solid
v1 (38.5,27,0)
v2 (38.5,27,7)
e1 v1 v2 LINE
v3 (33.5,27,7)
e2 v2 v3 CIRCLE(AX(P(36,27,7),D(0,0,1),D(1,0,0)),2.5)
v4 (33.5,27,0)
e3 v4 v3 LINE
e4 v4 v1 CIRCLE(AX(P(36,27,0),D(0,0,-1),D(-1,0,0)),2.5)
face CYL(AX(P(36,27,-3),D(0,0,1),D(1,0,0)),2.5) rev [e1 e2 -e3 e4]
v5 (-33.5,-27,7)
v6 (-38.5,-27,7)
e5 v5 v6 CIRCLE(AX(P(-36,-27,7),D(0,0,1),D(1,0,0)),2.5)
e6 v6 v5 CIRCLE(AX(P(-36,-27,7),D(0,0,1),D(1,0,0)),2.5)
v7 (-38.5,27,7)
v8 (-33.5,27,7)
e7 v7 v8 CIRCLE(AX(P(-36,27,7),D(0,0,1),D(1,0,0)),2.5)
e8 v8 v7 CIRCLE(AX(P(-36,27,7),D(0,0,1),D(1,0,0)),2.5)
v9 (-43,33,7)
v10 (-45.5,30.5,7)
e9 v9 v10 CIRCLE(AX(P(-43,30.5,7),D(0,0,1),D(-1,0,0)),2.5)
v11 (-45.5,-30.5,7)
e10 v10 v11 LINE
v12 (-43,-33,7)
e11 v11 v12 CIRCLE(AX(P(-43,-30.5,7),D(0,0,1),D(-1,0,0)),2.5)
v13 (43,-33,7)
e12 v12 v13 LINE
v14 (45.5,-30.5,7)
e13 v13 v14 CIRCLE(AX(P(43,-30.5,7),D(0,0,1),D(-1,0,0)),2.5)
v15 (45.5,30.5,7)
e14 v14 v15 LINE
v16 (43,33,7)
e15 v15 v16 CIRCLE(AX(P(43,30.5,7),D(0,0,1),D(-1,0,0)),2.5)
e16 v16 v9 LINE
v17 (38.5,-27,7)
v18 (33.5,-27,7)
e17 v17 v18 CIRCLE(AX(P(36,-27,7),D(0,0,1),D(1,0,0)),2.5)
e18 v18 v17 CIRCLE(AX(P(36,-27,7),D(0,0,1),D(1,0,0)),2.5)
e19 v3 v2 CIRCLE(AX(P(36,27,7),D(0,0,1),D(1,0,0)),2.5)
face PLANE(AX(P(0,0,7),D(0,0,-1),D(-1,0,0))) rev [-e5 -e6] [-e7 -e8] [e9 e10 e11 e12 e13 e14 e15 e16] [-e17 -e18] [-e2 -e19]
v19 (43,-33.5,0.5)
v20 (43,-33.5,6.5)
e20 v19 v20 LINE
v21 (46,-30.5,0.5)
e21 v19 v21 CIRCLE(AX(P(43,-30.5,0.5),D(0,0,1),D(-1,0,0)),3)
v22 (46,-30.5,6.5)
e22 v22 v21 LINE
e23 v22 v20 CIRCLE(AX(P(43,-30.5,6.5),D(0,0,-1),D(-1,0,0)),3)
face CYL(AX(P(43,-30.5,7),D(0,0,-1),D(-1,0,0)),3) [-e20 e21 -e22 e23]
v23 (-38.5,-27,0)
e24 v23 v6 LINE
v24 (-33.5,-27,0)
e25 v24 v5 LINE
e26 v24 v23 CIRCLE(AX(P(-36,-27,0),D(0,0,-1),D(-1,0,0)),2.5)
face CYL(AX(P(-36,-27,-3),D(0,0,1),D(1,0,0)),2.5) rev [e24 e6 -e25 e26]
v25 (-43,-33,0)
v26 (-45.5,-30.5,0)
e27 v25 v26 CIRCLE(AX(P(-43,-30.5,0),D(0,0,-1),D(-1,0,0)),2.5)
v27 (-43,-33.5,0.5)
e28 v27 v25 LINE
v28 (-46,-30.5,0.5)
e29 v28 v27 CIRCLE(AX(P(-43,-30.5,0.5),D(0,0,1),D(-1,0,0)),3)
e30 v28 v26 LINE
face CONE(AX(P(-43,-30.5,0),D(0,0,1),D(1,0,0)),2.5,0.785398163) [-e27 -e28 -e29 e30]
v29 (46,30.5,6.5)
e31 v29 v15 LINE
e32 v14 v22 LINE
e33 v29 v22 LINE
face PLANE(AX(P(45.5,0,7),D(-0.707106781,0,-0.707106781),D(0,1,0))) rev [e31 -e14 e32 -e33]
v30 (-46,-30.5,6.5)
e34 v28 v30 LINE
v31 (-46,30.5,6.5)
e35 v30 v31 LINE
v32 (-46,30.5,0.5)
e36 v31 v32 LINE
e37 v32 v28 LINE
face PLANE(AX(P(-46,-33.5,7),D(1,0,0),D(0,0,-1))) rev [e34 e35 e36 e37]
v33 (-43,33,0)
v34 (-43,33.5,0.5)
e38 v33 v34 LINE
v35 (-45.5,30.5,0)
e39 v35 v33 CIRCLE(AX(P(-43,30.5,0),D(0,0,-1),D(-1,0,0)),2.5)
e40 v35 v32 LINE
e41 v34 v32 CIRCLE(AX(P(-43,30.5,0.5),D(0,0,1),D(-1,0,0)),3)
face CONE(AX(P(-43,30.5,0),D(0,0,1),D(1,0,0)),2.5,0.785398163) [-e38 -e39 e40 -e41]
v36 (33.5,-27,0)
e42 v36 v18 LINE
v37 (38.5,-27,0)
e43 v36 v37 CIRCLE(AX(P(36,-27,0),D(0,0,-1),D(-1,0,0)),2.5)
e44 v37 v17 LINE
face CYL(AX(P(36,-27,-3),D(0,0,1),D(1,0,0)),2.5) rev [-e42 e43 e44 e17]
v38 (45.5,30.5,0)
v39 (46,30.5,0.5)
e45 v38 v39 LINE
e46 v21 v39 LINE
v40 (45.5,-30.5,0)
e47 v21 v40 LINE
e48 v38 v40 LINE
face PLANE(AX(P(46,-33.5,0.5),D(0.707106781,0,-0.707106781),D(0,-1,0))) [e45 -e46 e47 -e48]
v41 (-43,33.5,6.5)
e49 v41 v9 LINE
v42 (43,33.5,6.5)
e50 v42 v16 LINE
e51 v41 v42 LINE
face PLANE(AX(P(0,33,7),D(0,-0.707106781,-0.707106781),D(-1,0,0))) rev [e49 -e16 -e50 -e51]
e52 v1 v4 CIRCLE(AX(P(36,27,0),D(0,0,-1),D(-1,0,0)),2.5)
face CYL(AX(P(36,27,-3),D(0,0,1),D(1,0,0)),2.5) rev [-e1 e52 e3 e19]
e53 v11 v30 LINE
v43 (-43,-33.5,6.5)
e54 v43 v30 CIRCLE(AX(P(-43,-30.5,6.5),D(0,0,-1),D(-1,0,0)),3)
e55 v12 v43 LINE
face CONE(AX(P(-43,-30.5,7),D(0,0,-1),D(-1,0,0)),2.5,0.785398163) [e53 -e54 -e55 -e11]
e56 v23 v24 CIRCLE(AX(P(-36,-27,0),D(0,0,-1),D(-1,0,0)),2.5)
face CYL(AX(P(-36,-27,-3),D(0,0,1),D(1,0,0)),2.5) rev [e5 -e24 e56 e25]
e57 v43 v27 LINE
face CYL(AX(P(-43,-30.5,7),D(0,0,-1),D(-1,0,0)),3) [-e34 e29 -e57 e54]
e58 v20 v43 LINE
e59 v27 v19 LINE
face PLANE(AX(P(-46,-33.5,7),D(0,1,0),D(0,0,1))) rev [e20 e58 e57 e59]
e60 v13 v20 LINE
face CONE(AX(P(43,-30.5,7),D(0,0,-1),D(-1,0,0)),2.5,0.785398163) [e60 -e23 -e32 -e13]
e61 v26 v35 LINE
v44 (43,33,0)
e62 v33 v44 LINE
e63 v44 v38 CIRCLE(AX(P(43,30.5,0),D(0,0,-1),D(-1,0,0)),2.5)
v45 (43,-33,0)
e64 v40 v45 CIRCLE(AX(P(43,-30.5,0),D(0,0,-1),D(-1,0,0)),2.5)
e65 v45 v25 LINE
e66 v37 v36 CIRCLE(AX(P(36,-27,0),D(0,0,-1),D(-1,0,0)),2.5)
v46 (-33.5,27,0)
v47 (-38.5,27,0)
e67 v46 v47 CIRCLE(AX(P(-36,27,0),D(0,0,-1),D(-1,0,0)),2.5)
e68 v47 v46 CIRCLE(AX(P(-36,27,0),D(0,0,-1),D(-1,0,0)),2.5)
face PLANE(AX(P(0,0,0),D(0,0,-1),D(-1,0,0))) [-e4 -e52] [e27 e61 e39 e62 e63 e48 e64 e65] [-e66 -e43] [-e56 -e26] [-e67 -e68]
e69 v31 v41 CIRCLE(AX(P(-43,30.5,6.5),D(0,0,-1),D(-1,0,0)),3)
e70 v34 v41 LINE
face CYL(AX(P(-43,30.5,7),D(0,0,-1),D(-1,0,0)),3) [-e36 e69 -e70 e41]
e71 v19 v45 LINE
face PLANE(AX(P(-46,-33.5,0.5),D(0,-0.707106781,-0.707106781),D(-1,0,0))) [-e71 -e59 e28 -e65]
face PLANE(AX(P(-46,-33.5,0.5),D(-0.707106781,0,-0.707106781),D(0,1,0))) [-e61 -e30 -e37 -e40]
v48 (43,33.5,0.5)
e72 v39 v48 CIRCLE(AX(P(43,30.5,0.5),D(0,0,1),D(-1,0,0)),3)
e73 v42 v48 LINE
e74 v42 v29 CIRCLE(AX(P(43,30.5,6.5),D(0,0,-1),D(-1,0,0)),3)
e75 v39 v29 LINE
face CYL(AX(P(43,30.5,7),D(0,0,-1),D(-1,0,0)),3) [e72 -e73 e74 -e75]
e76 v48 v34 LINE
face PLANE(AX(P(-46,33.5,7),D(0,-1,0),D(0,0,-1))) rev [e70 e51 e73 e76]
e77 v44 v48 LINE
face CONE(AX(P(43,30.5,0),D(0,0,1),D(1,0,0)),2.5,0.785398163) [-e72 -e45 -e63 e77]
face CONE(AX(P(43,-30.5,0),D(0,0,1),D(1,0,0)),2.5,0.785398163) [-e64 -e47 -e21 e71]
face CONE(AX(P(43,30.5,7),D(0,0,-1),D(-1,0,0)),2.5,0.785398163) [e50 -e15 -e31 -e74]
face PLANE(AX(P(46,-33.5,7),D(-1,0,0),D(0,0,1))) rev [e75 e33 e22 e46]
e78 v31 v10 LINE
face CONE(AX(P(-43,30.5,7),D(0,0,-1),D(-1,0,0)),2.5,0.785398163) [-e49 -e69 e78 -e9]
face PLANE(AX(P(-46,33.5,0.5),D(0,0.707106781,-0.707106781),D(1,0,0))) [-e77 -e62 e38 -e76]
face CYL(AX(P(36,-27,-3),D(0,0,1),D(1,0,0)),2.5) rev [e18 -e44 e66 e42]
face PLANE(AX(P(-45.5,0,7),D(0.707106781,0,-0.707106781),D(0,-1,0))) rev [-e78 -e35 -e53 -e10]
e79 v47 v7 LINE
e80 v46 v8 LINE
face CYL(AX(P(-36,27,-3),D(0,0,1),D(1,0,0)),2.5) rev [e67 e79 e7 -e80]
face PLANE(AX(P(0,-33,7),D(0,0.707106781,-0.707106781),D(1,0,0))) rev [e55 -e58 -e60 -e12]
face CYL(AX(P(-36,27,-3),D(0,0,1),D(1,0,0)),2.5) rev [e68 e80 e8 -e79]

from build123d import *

# Parameters (mm, degrees)
SKETCH_1_W                  = 92
SKETCH_1_H                  = 67
EXTRUDE_1_DEPTH             = 7
FILLET_1_R                  = 3
SKETCH_2_R                  = 2.5
CUT_EXTRUDE_1_DEPTH         = 10
PATTERN_LINEAR_1_COUNT      = 2
PATTERN_LINEAR_1_PITCH      = 72
PATTERN_LINEAR_1_COUNT_DIR2 = 2
PATTERN_LINEAR_1_PITCH_DIR2 = 54
CHAMFER_1_SIZE              = 0.5


with BuildPart() as part:
    # 草图1 → 凸台-拉伸1 (new body)
    with BuildSketch(Plane.XY):
        Rectangle(SKETCH_1_W, SKETCH_1_H)
    extrude(amount=EXTRUDE_1_DEPTH)

    # 圆角1
    fillet_1_edges = [part.edges().sort_by_distance(p)[0] for p in [
        (46, -33.5, 3.5),
        (-46, -33.5, 3.5),
        (-46, 33.5, 3.5),
        (46, 33.5, 3.5),
    ]]
    fillet(fillet_1_edges, radius=FILLET_1_R)

    # 草图2 → 切除-拉伸1 (cut)
    with BuildSketch(Plane.XY.offset(7)):
        with Locations((-36, 27)):
            Circle(SKETCH_2_R)
    cut_extrude_1 = extrude(amount=-CUT_EXTRUDE_1_DEPTH, mode=Mode.SUBTRACT)

    # 阵列(线性)1: Cut-Extrude 1 2 × 2
    with Locations(*[(i * PATTERN_LINEAR_1_PITCH, -j * PATTERN_LINEAR_1_PITCH_DIR2, 0) for i in range(PATTERN_LINEAR_1_COUNT) for j in range(PATTERN_LINEAR_1_COUNT_DIR2) if (i, j) != (0, 0)]):
        add(cut_extrude_1, mode=Mode.SUBTRACT)

    # 倒角1
    chamfer_1_edges = [part.edges().sort_by_distance(p)[0] for p in [
        (46, 0, 0),
        (46, 0, 7),
        (0, -33.5, 0),
        (-46, 0, 0),
        (0, 33.5, 0),
        (-45.121320344, 32.621320344, 0),
        (45.121320344, 32.621320344, 0),
        (-45.121320344, -32.621320344, 0),
        (45.121320344, -32.621320344, 0),
        (0, -33.5, 7),
        (0, 33.5, 7),
        (-46, 0, 7),
        (-45.121320344, 32.621320344, 7),
        (45.121320344, 32.621320344, 7),
        (-45.121320344, -32.621320344, 7),
        (45.121320344, -32.621320344, 7),
    ]]
    chamfer(chamfer_1_edges, length=CHAMFER_1_SIZE)


solid = part.part
